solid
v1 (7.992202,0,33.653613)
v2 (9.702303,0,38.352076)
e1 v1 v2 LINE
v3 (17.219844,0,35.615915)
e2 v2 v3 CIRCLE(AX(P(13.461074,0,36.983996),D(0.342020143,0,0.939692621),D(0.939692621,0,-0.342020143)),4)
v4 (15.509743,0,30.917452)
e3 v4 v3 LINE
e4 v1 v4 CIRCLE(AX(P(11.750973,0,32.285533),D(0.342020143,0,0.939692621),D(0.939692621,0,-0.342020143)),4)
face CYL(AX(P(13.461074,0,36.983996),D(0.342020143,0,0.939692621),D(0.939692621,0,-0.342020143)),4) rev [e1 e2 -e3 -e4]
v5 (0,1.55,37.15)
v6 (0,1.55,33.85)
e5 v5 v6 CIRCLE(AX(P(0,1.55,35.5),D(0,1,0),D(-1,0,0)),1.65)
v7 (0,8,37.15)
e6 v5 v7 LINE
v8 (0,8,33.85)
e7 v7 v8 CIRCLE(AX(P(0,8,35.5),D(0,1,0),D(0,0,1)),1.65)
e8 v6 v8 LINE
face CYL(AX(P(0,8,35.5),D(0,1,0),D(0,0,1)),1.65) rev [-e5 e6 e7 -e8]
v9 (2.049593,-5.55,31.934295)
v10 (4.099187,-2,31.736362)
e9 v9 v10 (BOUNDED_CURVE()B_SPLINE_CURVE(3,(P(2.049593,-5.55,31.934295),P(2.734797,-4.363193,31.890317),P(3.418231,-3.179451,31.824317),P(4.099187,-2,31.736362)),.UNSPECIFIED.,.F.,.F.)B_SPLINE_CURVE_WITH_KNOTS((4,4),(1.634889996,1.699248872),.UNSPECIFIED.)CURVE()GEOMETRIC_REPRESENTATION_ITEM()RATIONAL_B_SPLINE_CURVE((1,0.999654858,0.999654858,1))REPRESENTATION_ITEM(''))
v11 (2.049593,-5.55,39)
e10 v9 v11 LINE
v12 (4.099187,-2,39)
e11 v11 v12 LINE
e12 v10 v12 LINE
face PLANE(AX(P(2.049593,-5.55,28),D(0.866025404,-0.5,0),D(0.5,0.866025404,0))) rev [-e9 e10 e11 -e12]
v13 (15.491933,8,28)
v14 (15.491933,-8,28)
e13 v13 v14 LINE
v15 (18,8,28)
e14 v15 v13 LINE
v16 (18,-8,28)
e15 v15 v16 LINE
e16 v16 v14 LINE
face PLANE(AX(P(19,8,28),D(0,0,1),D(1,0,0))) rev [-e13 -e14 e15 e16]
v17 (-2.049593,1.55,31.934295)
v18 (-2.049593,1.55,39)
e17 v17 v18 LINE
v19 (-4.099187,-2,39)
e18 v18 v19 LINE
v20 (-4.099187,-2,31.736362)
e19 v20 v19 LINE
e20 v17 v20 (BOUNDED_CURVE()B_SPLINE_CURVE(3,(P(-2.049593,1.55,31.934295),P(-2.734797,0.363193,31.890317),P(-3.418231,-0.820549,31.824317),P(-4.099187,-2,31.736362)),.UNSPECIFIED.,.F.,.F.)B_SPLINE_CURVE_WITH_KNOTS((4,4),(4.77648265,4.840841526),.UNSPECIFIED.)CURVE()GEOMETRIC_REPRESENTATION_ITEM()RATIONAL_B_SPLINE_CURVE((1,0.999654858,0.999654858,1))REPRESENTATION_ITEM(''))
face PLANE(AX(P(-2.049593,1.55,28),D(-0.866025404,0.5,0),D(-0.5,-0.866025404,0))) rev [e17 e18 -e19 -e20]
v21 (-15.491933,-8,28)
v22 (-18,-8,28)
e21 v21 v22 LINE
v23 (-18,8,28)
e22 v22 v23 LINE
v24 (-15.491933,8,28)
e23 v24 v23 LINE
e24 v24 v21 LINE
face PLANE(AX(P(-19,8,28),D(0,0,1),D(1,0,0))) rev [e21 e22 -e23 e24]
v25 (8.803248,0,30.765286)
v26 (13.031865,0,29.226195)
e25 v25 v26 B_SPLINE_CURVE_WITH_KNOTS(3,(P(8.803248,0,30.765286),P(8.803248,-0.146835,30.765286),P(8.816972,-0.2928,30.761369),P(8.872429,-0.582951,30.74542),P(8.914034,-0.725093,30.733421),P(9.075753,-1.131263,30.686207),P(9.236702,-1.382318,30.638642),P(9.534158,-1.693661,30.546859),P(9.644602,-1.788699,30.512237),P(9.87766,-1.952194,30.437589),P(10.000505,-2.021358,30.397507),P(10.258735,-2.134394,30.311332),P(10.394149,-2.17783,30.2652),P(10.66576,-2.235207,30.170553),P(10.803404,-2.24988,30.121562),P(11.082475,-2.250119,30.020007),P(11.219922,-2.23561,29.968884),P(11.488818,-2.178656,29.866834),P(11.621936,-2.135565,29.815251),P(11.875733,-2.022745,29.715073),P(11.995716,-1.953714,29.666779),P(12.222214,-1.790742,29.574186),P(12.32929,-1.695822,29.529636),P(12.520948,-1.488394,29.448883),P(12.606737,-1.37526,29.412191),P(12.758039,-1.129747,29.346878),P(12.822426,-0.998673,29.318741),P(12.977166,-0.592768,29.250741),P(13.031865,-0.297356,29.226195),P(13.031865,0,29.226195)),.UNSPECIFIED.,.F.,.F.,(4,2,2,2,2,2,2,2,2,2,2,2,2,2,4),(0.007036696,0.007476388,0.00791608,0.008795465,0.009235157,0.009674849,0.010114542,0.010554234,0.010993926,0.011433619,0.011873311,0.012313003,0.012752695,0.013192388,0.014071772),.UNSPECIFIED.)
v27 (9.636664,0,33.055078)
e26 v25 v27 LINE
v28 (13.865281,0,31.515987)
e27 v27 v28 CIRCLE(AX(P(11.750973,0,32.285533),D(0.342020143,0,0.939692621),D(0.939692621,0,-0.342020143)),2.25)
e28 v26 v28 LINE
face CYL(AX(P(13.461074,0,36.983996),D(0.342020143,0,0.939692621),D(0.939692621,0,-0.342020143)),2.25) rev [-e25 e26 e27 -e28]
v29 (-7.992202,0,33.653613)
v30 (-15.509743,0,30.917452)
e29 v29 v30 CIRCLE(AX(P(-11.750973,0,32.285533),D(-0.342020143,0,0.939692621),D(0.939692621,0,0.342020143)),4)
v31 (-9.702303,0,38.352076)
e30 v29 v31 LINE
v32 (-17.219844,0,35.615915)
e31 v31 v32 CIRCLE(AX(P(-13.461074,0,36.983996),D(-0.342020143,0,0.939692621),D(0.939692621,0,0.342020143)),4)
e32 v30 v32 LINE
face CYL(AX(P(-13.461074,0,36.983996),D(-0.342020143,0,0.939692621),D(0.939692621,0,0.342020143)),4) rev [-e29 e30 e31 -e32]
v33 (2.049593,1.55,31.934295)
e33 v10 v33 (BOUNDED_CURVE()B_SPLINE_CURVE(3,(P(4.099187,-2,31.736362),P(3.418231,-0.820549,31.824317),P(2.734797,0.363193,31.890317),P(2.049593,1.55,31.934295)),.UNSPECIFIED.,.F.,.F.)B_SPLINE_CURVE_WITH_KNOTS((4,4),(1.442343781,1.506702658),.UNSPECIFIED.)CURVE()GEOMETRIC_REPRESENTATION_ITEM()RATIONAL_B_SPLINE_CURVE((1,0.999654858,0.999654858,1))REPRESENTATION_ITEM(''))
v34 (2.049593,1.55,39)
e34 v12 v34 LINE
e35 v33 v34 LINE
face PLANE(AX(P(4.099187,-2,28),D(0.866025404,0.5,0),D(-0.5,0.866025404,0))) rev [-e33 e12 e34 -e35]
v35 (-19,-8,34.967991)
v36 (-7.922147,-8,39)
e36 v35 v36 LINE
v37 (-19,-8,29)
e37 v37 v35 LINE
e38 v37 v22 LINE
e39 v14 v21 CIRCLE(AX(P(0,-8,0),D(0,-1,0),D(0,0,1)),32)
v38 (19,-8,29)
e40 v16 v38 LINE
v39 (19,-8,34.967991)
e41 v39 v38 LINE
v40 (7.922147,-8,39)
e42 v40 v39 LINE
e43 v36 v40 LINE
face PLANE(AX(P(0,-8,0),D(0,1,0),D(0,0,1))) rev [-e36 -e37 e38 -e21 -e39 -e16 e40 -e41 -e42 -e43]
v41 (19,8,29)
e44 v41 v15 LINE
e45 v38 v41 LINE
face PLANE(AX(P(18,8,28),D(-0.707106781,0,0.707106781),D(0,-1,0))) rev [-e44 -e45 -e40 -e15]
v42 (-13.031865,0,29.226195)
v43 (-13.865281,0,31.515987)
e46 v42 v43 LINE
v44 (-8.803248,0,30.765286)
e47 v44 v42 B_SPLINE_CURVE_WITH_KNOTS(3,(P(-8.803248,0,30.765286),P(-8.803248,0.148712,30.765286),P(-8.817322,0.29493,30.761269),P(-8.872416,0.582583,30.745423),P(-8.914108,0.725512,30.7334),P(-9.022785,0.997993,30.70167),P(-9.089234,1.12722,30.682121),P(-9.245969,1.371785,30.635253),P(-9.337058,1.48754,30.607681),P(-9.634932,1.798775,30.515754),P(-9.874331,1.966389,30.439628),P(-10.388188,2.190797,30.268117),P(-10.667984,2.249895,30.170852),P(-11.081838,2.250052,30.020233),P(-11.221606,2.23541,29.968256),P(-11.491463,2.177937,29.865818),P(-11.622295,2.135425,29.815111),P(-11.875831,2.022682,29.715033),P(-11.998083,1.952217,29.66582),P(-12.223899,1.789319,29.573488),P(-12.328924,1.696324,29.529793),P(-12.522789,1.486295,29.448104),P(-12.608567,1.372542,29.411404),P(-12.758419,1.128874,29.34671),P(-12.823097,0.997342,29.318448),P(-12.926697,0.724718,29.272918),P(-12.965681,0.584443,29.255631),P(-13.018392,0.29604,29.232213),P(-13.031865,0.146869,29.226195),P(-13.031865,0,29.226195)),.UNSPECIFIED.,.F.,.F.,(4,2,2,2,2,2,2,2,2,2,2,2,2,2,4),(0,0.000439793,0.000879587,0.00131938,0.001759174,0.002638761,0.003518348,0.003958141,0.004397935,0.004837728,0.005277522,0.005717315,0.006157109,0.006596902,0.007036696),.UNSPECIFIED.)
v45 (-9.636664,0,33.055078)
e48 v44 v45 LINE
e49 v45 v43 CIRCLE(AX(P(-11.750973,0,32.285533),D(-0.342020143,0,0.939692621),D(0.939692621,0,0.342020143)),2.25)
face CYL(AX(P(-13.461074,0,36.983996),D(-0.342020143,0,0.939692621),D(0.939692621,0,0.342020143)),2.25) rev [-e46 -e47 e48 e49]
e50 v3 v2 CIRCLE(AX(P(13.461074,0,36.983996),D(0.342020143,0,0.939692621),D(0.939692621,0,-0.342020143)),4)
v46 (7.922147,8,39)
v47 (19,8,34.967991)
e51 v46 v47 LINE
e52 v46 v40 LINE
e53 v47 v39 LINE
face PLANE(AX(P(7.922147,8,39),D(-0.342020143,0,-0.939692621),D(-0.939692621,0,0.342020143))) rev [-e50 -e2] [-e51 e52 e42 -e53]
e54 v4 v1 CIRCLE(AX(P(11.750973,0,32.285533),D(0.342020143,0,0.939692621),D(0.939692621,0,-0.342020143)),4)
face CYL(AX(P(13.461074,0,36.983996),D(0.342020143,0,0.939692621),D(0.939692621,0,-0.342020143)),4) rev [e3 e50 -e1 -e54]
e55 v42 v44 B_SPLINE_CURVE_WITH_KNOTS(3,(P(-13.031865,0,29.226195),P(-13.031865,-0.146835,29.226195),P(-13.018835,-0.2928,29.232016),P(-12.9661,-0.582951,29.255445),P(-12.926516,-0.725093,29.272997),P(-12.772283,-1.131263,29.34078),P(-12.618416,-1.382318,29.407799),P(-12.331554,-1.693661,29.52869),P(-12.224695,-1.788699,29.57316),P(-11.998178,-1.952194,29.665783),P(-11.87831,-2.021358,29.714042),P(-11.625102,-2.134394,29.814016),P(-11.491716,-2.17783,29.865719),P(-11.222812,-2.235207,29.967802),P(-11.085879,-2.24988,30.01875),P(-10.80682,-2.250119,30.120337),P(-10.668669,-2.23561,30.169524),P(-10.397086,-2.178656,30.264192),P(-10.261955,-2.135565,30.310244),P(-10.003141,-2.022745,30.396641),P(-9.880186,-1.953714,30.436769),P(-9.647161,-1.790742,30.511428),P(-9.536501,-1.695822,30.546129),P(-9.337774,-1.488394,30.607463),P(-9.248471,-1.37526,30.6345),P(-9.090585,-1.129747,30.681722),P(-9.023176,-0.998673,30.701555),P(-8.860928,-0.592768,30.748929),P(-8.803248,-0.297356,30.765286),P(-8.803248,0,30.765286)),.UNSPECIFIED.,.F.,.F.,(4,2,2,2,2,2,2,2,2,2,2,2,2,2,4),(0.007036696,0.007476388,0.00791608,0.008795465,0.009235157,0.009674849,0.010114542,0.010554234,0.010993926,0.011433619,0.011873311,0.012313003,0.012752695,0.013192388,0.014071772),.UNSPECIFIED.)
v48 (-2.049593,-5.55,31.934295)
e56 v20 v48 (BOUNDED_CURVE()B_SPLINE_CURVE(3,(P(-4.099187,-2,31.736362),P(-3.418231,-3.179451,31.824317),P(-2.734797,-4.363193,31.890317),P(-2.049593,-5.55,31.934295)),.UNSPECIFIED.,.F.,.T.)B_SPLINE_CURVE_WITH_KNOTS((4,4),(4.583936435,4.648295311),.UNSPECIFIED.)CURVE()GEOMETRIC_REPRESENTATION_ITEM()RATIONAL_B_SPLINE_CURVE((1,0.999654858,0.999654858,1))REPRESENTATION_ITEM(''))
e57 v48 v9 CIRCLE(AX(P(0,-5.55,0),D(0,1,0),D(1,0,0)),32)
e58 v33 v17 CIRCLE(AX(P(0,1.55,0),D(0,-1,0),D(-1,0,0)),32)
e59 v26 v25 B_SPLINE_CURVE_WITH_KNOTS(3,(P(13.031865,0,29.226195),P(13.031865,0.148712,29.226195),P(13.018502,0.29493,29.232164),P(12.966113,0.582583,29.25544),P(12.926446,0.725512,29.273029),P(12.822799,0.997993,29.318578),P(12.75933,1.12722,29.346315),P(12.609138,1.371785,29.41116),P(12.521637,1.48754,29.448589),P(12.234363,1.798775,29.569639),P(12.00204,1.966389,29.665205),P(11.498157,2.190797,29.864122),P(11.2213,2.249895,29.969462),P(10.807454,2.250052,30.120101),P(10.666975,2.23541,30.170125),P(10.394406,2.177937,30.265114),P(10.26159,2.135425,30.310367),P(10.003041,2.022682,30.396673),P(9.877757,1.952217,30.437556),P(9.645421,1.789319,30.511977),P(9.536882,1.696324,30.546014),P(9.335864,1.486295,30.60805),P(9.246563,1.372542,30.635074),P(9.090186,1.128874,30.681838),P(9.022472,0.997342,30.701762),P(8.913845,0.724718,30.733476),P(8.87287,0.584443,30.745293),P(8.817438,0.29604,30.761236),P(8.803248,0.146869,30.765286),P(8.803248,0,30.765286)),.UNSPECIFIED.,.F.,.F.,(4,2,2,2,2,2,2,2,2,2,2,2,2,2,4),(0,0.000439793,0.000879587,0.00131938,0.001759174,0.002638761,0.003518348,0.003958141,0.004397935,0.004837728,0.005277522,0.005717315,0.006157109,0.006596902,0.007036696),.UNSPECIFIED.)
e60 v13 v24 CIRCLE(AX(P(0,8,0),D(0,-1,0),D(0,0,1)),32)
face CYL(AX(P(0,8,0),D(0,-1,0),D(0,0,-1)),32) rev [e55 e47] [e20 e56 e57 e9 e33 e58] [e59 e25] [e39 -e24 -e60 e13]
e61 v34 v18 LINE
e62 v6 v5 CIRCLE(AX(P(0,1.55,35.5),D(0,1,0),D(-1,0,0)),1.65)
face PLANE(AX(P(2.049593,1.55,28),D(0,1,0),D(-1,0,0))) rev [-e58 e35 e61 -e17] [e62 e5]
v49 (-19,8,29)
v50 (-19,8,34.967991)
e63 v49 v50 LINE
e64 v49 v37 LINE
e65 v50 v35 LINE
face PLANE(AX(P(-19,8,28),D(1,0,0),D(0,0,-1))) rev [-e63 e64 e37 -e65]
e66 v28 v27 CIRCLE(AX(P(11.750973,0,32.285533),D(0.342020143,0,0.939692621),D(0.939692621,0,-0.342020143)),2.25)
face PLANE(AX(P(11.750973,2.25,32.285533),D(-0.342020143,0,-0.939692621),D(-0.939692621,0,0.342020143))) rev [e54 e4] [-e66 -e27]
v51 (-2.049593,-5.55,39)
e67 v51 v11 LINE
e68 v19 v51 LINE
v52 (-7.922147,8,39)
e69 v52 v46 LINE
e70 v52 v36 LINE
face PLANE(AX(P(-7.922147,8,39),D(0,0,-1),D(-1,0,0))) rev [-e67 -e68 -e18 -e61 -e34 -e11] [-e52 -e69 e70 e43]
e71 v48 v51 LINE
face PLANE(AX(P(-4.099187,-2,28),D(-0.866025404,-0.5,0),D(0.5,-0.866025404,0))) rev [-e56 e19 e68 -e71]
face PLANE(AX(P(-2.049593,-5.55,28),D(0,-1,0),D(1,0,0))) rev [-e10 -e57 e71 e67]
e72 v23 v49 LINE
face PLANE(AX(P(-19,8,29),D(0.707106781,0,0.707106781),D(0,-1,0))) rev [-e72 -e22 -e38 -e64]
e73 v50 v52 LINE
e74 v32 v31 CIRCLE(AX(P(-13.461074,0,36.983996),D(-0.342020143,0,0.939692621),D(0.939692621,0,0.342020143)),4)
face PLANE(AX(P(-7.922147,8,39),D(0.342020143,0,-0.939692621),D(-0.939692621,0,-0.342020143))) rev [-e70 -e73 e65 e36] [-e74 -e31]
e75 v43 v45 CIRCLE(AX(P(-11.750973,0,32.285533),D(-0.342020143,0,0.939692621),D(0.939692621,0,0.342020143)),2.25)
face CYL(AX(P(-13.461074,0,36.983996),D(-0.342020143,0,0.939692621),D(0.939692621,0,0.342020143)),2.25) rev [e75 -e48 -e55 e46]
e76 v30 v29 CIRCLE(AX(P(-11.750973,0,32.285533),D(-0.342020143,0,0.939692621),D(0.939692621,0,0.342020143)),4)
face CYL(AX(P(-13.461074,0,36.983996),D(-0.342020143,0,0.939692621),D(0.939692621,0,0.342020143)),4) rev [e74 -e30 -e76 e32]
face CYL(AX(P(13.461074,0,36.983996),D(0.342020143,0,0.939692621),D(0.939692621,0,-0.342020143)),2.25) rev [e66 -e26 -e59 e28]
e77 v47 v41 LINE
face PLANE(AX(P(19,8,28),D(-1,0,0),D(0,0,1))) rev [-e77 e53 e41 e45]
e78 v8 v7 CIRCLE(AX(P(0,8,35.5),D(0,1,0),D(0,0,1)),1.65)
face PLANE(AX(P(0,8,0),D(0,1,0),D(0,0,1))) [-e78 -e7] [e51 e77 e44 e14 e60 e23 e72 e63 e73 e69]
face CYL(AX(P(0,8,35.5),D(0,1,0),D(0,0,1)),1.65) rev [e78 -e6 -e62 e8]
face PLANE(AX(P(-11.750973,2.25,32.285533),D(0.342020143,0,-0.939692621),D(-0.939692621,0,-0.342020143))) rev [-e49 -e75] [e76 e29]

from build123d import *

# Parameters (mm, degrees)
BOSS_EXTRUDE1_DEPTH                                  = 8
CUT_EXTRUDE2_DEPTH                                   = 24.366642891
M4_TAPPED_HOLE1_D                                    = 3.3
M4_TAPPED_HOLE1_DEPTH                                = 11.5
M4_TAPPED_HOLE1_TIP                                  = 0.991420021
HOLE_SIZE_PER_SOCKET_HEAD_CAP_SCREW_TYPE_D           = 4.5
HOLE_SIZE_PER_SOCKET_HEAD_CAP_SCREW_TYPE_CBORE_D     = 8
HOLE_SIZE_PER_SOCKET_HEAD_CAP_SCREW_TYPE_CBORE_DEPTH = 5
CHAMFER2_SIZE                                        = 1


with BuildPart() as part:
    # Sketch1 → Boss-Extrude1 (new, symmetric)
    with BuildSketch(Plane(origin=(0, 0, 0), x_dir=(1, 0, 0), z_dir=(0, 1, 0))):
        with BuildLine():
            Line((-7.922147119, -39), (7.922147119, -39))
            Line((7.922147119, -39), (19, -34.967991292))
            Line((19, -34.967991292), (19, -28))
            Line((19, -28), (15.491933385, -28))
            ThreePointArc((15.491933385, -28), (0, -32), (-15.491933385, -28))
            Line((-15.491933385, -28), (-19, -28))
            Line((-19, -28), (-19, -34.967991292))
            Line((-19, -34.967991292), (-7.922147119, -39))
        make_face()
    extrude(amount=BOSS_EXTRUDE1_DEPTH, both=True)

    # Sketch2 → Cut-Extrude2 (cut, through all)
    with BuildSketch(Plane.XY.offset(39)):
        Polygon((4.099186911, -2), (2.049593456, 1.55), (-2.049593456, 1.55), (-4.099186911, -2), (-2.049593456, -5.55), (2.049593456, -5.55), align=None)
    extrude(amount=-CUT_EXTRUDE2_DEPTH, mode=Mode.SUBTRACT)

    # M4 Tapped Hole1
    with Locations(Plane(origin=(0, 8, 0), x_dir=(1, 0, 0), z_dir=(0, 1, 0))):
        with Locations((0, -35.5)):
            Hole(M4_TAPPED_HOLE1_D / 2, depth=M4_TAPPED_HOLE1_DEPTH)
            with Locations((0, 0, -(M4_TAPPED_HOLE1_DEPTH + M4_TAPPED_HOLE1_TIP / 2))):  # 118° drill point
                Cone(0, M4_TAPPED_HOLE1_D / 2, M4_TAPPED_HOLE1_TIP, mode=Mode.SUBTRACT)

    # Hole size per socket head cap screw type 2 (through all)
    with Locations(Plane(origin=(-13.461073559, 0, 36.983995646), x_dir=(0.9396926207859081, 0, 0.34202014332566943), z_dir=(-0.34202014332566943, 0, 0.9396926207859081))):
        with Locations((0, 0)):
            hole_size_per_socket_head_cap_screw_type = CounterBoreHole(HOLE_SIZE_PER_SOCKET_HEAD_CAP_SCREW_TYPE_D / 2, HOLE_SIZE_PER_SOCKET_HEAD_CAP_SCREW_TYPE_CBORE_D / 2, HOLE_SIZE_PER_SOCKET_HEAD_CAP_SCREW_TYPE_CBORE_DEPTH)

    # Mirror3: Hole size per socket head cap screw type 2 across plane
    add(hole_size_per_socket_head_cap_screw_type.mirror(Plane(origin=(0, 0, 0), x_dir=(0, 0, 1), z_dir=(1, 0, 0))), mode=Mode.SUBTRACT)

    # Chamfer2
    chamfer2_edges = [part.edges().sort_by_distance(p)[0] for p in [
        (-19, 0, 28),
        (19, 0, 28),
    ]]
    chamfer(chamfer2_edges, length=CHAMFER2_SIZE)


solid = part.part
